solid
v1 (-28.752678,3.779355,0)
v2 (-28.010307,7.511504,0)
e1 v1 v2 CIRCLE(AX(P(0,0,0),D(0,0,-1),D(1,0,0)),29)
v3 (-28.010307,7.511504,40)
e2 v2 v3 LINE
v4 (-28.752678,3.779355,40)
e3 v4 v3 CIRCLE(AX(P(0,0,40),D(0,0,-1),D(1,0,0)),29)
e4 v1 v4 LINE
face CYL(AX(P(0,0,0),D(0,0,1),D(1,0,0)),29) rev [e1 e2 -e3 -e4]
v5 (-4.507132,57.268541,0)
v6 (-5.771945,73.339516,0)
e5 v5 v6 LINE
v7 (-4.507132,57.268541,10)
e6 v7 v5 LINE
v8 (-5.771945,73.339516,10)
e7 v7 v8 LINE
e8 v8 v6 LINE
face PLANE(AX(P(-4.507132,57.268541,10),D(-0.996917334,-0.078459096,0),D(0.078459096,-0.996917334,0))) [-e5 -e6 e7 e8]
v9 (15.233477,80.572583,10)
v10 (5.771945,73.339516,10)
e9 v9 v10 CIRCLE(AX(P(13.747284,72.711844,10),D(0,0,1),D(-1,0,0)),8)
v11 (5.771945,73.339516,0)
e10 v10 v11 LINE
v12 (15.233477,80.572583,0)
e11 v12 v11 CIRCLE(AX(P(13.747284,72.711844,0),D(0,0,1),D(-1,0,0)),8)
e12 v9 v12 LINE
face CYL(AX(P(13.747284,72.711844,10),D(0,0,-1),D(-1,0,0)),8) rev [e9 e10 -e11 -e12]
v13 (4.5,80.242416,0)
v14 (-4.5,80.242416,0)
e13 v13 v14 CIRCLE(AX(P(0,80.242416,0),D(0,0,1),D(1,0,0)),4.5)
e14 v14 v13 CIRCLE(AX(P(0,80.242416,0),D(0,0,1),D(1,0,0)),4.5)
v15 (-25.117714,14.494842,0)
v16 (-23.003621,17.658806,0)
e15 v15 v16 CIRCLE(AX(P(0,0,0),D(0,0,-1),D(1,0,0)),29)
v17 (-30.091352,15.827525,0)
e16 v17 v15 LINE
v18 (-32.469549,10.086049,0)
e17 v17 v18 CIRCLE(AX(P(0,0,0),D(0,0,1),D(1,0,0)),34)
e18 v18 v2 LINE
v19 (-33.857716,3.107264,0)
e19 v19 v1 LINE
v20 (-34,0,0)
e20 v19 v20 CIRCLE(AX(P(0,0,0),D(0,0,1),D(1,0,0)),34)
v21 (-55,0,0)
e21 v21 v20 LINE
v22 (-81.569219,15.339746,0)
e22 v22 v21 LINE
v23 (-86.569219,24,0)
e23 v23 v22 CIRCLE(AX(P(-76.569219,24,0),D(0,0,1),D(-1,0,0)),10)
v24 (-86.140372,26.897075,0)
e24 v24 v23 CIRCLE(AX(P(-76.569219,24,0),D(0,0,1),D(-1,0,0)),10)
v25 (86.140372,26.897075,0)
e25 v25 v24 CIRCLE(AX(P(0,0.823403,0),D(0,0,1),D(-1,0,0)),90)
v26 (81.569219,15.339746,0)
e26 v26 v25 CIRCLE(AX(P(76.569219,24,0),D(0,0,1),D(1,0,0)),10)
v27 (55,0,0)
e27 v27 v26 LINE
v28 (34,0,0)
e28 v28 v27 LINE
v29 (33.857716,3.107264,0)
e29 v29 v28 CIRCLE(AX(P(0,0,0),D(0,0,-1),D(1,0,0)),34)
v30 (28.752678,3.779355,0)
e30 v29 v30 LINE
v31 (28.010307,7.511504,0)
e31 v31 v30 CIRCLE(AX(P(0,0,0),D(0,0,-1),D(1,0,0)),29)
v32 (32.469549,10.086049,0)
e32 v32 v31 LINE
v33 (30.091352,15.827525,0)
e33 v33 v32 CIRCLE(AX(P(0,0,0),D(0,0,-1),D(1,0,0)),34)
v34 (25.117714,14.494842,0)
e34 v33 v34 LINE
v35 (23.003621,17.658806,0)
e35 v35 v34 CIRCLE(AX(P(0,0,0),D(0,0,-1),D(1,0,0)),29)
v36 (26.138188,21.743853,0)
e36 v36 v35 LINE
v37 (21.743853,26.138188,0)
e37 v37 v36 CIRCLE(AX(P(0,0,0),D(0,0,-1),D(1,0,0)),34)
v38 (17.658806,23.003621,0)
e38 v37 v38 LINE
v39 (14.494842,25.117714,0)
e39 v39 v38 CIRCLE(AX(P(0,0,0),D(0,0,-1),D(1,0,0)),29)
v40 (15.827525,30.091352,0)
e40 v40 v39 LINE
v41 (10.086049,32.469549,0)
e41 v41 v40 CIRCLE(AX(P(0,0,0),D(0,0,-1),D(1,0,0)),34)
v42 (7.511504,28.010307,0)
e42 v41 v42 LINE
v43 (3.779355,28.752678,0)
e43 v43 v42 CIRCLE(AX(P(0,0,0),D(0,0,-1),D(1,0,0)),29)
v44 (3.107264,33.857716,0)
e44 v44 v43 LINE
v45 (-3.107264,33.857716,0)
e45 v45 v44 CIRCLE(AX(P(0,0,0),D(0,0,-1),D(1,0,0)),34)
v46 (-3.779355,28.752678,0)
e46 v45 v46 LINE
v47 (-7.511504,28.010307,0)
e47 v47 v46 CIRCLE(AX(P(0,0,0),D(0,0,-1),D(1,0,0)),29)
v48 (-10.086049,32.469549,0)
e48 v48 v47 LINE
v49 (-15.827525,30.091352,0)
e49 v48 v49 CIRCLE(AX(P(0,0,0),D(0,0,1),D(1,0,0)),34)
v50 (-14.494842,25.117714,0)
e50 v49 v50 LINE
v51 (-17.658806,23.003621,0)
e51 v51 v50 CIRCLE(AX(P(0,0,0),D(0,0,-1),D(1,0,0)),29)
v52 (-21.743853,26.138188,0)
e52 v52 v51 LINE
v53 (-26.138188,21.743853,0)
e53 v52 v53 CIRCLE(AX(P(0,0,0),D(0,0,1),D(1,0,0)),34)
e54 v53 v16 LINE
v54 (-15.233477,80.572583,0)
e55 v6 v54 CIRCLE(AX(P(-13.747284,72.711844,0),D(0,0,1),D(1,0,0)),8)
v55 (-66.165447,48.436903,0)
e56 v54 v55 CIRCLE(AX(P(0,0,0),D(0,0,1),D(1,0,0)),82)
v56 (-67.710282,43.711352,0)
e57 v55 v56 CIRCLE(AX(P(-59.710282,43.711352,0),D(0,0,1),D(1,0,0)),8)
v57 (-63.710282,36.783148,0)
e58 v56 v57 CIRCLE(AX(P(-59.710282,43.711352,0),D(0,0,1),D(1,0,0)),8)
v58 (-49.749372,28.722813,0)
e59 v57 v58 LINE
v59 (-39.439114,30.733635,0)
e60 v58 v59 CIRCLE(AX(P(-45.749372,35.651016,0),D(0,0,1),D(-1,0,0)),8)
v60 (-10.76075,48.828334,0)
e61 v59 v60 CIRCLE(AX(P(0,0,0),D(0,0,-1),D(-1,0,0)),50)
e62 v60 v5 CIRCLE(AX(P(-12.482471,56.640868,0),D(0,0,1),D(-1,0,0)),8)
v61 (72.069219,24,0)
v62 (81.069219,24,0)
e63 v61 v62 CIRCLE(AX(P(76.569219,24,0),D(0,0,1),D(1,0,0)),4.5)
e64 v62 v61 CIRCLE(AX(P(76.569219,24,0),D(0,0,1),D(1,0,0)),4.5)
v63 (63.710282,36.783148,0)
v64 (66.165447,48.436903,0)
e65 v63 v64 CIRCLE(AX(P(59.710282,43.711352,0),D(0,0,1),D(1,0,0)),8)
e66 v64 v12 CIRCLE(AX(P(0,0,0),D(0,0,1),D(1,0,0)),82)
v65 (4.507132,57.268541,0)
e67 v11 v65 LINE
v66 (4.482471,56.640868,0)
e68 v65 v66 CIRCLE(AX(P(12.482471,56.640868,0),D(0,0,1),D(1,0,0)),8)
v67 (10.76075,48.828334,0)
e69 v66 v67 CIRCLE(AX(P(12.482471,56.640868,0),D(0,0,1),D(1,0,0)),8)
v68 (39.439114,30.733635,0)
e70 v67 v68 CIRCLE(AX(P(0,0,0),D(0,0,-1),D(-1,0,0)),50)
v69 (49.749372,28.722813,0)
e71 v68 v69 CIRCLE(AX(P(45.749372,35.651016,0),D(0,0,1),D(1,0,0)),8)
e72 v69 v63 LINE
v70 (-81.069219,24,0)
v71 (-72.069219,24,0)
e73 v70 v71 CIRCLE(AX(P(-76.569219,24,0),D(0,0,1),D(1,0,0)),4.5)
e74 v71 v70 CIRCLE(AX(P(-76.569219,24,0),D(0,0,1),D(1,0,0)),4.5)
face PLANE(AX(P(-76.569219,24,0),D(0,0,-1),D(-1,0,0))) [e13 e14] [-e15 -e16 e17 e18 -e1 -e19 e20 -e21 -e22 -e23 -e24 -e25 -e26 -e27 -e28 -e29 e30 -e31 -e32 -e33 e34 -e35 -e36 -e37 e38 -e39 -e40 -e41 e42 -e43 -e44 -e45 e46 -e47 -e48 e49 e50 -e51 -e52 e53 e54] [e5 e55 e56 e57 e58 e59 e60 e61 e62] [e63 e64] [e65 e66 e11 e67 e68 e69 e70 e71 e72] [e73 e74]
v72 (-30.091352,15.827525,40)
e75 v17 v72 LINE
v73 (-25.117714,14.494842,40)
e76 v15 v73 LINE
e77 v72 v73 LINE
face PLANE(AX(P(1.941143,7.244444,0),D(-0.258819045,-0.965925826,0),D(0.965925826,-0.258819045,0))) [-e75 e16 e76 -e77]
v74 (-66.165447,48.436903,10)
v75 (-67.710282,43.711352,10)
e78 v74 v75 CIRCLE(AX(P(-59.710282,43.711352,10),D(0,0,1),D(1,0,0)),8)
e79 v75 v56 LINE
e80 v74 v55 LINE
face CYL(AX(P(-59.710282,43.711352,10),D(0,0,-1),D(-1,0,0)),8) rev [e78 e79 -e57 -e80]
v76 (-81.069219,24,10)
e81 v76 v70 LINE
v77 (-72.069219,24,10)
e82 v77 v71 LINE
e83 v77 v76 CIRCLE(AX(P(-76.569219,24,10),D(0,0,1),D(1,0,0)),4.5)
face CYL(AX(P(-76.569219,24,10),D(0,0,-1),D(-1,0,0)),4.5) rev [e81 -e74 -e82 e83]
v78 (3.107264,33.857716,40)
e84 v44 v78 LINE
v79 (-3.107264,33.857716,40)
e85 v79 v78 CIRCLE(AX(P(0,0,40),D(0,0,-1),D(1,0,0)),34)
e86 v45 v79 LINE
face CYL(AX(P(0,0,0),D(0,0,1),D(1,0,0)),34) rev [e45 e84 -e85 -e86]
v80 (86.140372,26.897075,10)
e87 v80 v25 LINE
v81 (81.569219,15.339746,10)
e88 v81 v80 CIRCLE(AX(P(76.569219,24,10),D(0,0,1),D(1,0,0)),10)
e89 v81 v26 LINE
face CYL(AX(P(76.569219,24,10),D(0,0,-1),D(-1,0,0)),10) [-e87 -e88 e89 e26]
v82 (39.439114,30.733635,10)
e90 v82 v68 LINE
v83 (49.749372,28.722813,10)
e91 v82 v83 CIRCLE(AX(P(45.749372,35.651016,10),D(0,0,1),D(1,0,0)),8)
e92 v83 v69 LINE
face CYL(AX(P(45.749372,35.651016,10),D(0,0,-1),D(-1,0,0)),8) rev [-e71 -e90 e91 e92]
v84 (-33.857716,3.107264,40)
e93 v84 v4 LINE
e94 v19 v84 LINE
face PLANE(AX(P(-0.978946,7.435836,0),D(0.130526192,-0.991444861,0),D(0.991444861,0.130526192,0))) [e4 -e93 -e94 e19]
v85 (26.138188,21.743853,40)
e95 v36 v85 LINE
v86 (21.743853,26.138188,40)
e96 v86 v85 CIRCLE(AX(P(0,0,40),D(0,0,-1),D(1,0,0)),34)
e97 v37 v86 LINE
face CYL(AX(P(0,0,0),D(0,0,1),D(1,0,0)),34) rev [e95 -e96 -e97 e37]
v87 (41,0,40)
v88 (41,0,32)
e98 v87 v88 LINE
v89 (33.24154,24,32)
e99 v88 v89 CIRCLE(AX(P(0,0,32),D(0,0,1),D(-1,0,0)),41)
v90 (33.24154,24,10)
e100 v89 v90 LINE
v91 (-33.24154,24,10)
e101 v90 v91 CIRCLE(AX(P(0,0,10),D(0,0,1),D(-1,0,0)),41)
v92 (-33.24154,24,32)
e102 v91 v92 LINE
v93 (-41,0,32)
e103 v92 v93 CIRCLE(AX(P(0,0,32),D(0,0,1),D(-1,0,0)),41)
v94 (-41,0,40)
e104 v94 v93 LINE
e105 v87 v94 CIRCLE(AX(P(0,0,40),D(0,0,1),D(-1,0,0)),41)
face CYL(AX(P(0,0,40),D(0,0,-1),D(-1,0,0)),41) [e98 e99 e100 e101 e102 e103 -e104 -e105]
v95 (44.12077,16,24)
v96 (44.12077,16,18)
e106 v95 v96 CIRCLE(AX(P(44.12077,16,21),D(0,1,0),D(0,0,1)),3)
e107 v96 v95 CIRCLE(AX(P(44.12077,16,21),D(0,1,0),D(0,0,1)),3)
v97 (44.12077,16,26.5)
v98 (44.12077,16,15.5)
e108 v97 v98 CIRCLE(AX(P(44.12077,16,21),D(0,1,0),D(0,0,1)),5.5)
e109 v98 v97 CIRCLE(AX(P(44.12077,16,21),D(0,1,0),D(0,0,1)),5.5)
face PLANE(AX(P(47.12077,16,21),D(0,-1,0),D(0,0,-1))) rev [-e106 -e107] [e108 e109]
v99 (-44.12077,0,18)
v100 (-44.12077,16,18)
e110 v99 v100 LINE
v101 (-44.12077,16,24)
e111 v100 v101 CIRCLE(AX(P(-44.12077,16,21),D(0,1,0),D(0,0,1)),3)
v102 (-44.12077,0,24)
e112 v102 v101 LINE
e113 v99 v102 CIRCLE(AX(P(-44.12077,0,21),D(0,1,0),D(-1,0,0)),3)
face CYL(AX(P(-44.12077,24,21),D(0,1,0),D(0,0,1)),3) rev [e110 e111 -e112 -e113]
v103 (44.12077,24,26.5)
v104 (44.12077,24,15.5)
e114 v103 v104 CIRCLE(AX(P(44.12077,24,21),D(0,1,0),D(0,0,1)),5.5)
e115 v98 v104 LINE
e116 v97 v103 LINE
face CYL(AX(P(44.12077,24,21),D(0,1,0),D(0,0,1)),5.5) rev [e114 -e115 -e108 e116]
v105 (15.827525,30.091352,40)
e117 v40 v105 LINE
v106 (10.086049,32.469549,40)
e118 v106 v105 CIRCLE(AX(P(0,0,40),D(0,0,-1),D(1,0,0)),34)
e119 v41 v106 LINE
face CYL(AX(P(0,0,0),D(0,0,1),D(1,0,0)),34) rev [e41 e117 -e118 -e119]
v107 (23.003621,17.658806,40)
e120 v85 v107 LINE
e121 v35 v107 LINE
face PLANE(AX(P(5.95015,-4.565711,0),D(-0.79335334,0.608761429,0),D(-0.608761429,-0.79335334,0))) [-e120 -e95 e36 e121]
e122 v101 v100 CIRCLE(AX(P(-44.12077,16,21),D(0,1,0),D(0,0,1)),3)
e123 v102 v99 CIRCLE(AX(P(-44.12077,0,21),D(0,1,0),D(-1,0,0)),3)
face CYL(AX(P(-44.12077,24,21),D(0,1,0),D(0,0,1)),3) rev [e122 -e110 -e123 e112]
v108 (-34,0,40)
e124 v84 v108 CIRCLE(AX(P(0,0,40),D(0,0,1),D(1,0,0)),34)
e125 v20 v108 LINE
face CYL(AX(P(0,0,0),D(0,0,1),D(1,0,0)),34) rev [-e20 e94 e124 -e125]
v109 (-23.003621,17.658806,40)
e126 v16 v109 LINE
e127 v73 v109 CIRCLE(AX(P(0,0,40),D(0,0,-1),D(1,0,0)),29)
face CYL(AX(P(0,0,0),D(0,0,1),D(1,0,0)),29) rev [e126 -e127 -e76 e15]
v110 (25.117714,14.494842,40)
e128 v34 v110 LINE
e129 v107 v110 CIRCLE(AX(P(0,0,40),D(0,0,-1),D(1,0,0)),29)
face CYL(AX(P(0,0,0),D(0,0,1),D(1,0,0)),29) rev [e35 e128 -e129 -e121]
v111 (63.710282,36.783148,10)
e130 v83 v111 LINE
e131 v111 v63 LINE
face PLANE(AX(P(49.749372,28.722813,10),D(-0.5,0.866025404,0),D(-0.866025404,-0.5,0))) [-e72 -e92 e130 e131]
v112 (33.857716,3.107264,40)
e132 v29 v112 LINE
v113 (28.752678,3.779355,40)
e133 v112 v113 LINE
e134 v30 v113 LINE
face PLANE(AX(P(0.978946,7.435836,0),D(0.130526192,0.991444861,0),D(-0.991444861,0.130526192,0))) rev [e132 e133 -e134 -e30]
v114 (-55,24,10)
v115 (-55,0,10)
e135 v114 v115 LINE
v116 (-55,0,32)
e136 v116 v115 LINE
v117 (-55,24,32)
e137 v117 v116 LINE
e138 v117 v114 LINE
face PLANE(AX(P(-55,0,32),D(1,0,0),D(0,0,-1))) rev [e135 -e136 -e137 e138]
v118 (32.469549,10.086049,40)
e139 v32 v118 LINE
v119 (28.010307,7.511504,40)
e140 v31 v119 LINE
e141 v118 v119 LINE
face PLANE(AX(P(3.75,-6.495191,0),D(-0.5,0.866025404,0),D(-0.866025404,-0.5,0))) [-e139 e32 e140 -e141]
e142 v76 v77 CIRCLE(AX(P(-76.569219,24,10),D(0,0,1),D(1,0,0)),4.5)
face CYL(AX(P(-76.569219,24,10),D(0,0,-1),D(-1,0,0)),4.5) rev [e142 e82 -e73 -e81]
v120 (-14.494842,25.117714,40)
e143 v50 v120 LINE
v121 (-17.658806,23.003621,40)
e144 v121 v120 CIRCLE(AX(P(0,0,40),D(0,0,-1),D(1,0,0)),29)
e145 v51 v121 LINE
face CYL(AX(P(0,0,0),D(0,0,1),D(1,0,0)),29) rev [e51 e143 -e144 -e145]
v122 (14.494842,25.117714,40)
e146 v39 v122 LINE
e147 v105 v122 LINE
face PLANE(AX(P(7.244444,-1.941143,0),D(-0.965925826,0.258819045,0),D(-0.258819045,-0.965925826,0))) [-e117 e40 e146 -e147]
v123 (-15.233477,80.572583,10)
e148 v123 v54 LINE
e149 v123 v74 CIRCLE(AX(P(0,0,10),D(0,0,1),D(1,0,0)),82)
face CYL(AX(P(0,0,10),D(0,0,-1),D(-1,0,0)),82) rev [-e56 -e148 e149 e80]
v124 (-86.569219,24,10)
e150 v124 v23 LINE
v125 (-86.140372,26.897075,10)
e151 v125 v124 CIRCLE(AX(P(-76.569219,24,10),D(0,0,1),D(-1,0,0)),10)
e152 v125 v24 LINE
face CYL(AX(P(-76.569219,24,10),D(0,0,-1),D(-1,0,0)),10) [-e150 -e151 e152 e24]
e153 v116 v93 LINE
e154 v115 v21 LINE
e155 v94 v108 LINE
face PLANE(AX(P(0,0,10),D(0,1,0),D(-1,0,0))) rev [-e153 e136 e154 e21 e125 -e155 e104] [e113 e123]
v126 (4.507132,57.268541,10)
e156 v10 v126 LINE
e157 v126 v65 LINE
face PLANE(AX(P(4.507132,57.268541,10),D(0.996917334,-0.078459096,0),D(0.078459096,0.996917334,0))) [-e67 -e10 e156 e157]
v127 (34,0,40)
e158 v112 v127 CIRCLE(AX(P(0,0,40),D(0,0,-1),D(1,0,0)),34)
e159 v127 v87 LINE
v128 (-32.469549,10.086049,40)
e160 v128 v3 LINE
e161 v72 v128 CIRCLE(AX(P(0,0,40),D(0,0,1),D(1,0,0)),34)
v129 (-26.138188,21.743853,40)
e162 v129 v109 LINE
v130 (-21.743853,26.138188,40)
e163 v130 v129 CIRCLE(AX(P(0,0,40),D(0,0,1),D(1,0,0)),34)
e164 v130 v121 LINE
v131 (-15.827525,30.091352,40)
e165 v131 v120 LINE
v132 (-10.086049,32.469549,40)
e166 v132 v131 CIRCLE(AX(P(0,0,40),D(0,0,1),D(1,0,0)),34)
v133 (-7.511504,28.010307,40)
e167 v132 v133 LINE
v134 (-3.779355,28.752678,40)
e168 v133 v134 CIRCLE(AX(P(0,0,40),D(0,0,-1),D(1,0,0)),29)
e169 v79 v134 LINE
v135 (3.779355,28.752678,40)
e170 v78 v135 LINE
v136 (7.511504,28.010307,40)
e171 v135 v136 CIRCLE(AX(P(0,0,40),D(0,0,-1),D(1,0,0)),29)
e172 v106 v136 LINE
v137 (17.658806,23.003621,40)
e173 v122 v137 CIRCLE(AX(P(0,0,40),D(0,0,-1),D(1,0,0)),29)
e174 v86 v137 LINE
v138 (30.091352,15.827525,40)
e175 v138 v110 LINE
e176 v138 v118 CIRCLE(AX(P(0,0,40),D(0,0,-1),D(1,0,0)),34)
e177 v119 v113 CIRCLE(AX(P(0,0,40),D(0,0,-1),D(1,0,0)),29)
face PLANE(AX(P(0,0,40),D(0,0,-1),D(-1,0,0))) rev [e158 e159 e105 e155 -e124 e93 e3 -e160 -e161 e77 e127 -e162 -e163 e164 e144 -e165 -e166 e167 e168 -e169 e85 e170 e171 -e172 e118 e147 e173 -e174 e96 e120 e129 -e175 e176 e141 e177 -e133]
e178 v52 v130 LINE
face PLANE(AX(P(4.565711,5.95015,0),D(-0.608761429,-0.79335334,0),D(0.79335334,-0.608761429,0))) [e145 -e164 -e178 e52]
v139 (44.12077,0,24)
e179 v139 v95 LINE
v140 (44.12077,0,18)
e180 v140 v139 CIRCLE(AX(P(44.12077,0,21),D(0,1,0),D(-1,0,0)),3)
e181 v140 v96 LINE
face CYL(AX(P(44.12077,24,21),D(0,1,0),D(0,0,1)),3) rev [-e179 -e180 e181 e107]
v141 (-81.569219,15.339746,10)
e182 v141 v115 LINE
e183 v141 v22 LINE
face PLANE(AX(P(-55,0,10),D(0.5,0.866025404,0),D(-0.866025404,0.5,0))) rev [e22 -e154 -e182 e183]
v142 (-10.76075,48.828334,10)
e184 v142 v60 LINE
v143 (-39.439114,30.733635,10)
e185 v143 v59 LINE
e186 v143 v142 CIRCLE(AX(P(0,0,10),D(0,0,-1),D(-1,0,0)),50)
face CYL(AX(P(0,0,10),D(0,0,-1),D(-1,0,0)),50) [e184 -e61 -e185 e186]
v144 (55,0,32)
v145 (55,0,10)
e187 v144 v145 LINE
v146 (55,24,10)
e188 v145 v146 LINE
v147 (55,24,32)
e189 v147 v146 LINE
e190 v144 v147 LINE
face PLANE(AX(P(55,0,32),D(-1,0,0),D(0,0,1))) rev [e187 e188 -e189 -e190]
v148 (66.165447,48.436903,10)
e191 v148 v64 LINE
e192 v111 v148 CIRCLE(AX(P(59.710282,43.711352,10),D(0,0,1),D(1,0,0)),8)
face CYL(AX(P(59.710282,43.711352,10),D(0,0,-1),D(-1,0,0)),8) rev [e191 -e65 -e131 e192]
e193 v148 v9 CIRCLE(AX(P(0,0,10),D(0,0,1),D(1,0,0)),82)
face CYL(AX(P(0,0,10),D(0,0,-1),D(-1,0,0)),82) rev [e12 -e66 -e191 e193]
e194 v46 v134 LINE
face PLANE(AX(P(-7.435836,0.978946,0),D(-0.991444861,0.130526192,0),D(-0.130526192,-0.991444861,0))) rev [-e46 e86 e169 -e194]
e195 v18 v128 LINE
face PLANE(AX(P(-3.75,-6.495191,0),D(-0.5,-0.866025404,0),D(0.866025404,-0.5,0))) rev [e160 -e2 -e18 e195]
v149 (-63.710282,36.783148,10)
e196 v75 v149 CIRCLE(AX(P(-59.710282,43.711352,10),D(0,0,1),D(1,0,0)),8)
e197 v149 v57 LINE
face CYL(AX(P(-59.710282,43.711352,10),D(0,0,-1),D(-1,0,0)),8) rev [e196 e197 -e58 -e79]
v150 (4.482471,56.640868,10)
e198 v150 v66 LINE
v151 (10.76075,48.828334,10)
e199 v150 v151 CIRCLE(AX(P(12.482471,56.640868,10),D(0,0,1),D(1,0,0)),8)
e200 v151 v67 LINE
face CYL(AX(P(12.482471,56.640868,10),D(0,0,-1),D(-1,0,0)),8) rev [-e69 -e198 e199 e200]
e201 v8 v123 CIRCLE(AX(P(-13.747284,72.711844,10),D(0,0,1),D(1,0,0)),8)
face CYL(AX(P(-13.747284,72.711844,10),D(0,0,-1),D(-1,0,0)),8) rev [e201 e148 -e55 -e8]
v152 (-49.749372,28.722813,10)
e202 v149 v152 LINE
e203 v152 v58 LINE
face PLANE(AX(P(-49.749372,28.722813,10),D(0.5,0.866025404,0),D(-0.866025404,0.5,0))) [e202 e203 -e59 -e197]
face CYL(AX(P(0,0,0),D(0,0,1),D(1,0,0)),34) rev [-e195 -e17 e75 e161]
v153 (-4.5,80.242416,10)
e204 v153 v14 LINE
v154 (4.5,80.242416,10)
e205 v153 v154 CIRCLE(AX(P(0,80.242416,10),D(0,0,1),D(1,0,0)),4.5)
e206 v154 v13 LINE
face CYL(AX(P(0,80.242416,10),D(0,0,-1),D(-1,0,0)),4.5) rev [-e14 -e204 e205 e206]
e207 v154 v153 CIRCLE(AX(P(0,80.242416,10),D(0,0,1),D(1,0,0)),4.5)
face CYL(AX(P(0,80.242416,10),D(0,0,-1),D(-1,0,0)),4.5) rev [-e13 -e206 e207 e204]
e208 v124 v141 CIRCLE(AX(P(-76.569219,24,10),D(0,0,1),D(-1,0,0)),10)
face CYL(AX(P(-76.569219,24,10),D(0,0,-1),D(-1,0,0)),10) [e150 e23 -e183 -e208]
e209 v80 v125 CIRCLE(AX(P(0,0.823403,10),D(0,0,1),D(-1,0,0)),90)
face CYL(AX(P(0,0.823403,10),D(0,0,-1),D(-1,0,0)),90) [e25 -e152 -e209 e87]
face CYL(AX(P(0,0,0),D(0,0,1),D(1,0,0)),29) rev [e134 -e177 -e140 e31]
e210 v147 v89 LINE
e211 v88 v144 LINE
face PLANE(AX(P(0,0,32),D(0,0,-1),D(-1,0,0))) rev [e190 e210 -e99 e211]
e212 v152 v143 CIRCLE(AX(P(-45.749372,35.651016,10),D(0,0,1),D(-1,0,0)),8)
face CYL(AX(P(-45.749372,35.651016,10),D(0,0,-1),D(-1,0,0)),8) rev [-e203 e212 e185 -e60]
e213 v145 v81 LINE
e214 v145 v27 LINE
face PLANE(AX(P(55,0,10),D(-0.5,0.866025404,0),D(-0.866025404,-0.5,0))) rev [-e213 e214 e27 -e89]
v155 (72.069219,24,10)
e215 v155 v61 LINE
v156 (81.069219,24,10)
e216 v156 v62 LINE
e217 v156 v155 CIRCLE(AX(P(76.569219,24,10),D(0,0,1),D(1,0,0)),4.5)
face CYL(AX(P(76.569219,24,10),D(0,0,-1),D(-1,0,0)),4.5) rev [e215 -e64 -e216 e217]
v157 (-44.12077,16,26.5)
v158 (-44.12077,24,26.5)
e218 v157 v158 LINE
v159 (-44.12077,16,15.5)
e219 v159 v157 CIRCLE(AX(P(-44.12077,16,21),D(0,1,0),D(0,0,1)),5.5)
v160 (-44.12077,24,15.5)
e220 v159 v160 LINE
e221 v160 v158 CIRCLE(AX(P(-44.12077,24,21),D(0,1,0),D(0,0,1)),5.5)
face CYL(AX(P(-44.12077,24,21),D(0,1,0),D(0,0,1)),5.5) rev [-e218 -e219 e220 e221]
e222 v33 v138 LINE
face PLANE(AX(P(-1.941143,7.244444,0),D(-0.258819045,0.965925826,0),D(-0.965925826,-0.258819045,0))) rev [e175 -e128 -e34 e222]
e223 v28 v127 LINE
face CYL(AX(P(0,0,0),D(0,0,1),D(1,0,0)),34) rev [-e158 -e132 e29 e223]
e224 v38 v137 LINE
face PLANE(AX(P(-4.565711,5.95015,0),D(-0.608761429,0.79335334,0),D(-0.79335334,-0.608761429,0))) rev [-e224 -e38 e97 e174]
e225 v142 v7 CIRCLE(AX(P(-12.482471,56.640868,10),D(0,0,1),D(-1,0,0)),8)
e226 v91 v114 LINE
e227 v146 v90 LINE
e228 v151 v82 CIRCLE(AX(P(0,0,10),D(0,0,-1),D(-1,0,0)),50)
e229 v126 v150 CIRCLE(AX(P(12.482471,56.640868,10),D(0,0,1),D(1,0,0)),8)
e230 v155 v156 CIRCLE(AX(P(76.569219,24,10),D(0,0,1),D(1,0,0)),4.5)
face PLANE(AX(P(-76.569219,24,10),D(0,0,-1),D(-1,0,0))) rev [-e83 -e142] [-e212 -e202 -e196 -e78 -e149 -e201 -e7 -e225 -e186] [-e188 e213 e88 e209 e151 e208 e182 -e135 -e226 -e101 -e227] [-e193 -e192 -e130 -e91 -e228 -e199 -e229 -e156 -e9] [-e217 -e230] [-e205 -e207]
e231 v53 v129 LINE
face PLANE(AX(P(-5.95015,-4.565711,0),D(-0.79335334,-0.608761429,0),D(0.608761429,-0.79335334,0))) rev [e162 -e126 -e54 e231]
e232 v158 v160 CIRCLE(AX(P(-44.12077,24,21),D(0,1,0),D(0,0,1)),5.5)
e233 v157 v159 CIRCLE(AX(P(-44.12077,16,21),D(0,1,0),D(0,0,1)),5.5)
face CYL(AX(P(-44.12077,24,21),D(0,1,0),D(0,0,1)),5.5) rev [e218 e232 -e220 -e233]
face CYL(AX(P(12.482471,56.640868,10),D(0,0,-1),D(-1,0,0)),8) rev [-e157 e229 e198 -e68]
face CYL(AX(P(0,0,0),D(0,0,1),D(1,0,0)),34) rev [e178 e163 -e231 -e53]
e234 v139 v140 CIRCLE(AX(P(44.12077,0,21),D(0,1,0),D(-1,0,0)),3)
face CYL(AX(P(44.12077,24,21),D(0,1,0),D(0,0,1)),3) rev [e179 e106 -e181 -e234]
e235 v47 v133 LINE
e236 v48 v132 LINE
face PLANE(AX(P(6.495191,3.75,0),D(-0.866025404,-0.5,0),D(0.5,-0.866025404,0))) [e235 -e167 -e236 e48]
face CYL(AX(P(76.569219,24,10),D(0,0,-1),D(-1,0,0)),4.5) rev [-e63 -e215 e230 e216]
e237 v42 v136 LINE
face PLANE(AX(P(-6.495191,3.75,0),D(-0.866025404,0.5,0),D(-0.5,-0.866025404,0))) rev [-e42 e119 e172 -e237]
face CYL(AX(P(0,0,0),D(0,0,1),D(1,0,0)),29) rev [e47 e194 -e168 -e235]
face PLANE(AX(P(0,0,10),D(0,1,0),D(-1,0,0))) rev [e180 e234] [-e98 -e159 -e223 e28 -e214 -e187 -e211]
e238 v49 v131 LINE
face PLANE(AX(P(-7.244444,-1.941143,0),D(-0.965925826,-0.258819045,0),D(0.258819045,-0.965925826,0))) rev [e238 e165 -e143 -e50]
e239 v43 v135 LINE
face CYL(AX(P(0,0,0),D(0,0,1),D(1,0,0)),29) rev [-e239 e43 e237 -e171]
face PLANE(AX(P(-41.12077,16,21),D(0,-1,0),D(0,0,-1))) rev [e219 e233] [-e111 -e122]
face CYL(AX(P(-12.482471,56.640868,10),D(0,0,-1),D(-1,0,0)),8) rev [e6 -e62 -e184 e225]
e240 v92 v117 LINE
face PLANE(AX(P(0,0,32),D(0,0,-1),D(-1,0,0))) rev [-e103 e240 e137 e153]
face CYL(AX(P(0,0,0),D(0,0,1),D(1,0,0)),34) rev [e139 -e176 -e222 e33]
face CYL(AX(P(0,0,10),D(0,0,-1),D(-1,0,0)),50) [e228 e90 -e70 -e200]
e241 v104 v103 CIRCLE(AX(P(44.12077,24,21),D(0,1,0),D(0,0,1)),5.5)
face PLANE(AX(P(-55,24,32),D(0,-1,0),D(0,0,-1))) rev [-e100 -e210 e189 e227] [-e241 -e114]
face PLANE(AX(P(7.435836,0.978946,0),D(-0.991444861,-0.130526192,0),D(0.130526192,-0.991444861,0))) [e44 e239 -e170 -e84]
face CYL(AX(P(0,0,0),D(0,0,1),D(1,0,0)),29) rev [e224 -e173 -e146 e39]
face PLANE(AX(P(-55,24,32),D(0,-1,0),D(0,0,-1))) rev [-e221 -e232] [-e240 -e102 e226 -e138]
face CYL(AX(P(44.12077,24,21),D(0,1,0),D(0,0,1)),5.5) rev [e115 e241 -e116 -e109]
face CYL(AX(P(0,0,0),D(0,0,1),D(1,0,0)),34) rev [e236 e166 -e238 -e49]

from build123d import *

# Parameters (mm, degrees)
SECTOR_PLATE_SKETCH_R          = 4.5
SECTOR_PLATE_DEPTH             = 10
MOUNTING_LUG_SKETCH_W          = 110
MOUNTING_LUG_SKETCH_H          = 24
MOUNTING_LUGS_DEPTH            = 22
HALF_HUB_DEPTH                 = 30
LUG_C_BORE_HOLES_6_D           = 6
LUG_C_BORE_HOLES_6_DEPTH       = 99.968745116
LUG_C_BORE_HOLES_6_CBORE_D     = 11
LUG_C_BORE_HOLES_6_CBORE_DEPTH = 8
INTERNAL_SPLINE_CUT_DEPTH      = 132.69328114


with BuildPart() as part:
    # Sector Plate Sketch → Sector Plate (new body)
    with BuildSketch(Plane.XY):
        with BuildLine():
            Line((0, 0), (55, 0))
            Line((55, 0), (81.569219382, 15.339745962))
            ThreePointArc((81.569219382, 15.339745962), (85.868282889, 20.322036175), (86.140371804, 26.897074611))
            ThreePointArc((86.140371804, 26.897074611), (0, 90.823403113), (-86.140371804, 26.897074611))
            ThreePointArc((-86.140371804, 26.897074611), (-85.868282889, 20.322036175), (-81.569219382, 15.339745962))
            Line((-81.569219382, 15.339745962), (-55, 0))
            Line((-55, 0), (0, 0))
        make_face()
        with Locations((-76.569219382, 24)):
            Circle(SECTOR_PLATE_SKETCH_R, mode=Mode.SUBTRACT)
        with Locations((76.569219382, 24)):
            Circle(SECTOR_PLATE_SKETCH_R, mode=Mode.SUBTRACT)
        with Locations((0, 80.242416194)):
            Circle(SECTOR_PLATE_SKETCH_R, mode=Mode.SUBTRACT)
        with BuildLine():
            Line((4.507131906, 57.26854077), (5.77194511, 73.33951629))
            ThreePointArc((5.77194511, 73.33951629), (8.888624682, 79.067426249), (15.233476621, 80.572583365))
            ThreePointArc((15.233476621, 80.572583365), (43.756390305, 69.34968138), (66.165447339, 48.436903064))
            ThreePointArc((66.165447339, 48.436903064), (67.538443843, 42.062146233), (63.710281745, 36.783148315))
            Line((63.710281745, 36.783148315), (49.749371855, 28.722813233))
            ThreePointArc((49.749371855, 28.722813233), (44.217975712, 27.798957762), (39.439113668, 30.733634882))
            ThreePointArc((39.439113668, 30.733634882), (26.680725796, 42.286391085), (10.760750496, 48.828334487))
            ThreePointArc((10.760750496, 48.828334487), (6.054600974, 51.878253977), (4.507131906, 57.26854077))
        make_face(mode=Mode.SUBTRACT)
        with BuildLine():
            Line((-4.507131906, 57.26854077), (-5.77194511, 73.33951629))
            ThreePointArc((-5.77194511, 73.33951629), (-8.888624682, 79.067426249), (-15.233476621, 80.572583365))
            ThreePointArc((-15.233476621, 80.572583365), (-43.756390305, 69.34968138), (-66.165447339, 48.436903064))
            ThreePointArc((-66.165447339, 48.436903064), (-67.538443843, 42.062146233), (-63.710281745, 36.783148315))
            Line((-63.710281745, 36.783148315), (-49.749371855, 28.722813233))
            ThreePointArc((-49.749371855, 28.722813233), (-44.217975712, 27.798957762), (-39.439113668, 30.733634882))
            ThreePointArc((-39.439113668, 30.733634882), (-26.680725796, 42.286391085), (-10.760750496, 48.828334487))
            ThreePointArc((-10.760750496, 48.828334487), (-6.054600974, 51.878253977), (-4.507131906, 57.26854077))
        make_face(mode=Mode.SUBTRACT)
    extrude(amount=SECTOR_PLATE_DEPTH)

    # Mounting Lug Sketch → Mounting Lugs (add)
    with BuildSketch(Plane.XY.offset(10)):
        with Locations((0, 12)):
            Rectangle(MOUNTING_LUG_SKETCH_W, MOUNTING_LUG_SKETCH_H)
    extrude(amount=MOUNTING_LUGS_DEPTH)

    # Half Hub Sketch → Half Hub (add)
    with BuildSketch(Plane.XY.offset(10)):
        with BuildLine():
            Line((-41, 0), (41, 0))
            ThreePointArc((41, 0), (0, 41), (-41, 0))
        make_face()
    extrude(amount=HALF_HUB_DEPTH)

    # Lug C'Bore Holes Ø6
    with Locations(Plane(origin=(-44.120770139, 24, 21), x_dir=(0, 0, 1), z_dir=(0, 1, 0))):
        with Locations((0, 0), (0, 88.241540278)):
            CounterBoreHole(LUG_C_BORE_HOLES_6_D / 2, LUG_C_BORE_HOLES_6_CBORE_D / 2, LUG_C_BORE_HOLES_6_CBORE_DEPTH, depth=LUG_C_BORE_HOLES_6_DEPTH)

    # Internal Spline Sketch → Internal Spline Cut (cut, through all)
    with BuildSketch(Plane.XY.offset(40)):
        with BuildLine():
            ThreePointArc((3.107264378, 33.857715636), (0, 34), (-3.107264378, 33.857715636))
            Line((-3.107264378, 33.857715636), (-3.779355377, 28.752677665))
            ThreePointArc((-3.779355377, 28.752677665), (-5.657619338, 28.442773132), (-7.511504299, 28.010307088))
            Line((-7.511504299, 28.010307088), (-10.08604887, 32.469549091))
            ThreePointArc((-10.08604887, 32.469549091), (-13.0112367, 31.411904105), (-15.827524793, 30.091351896))
            Line((-15.827524793, 30.091351896), (-14.494842458, 25.117713712))
            ThreePointArc((-14.494842458, 25.117713712), (-16.111536758, 24.112618757), (-17.658805539, 23.00362117))
            Line((-17.658805539, 23.00362117), (-21.743852609, 26.138188034))
            ThreePointArc((-21.743852609, 26.138188034), (-24.04163056, 24.04163056), (-26.138188034, 21.743852609))
            Line((-26.138188034, 21.743852609), (-23.00362117, 17.658805539))
            ThreePointArc((-23.00362117, 17.658805539), (-24.112618757, 16.111536758), (-25.117713712, 14.494842458))
            Line((-25.117713712, 14.494842458), (-30.091351896, 15.827524793))
            ThreePointArc((-30.091351896, 15.827524793), (-31.411904105, 13.0112367), (-32.469549091, 10.08604887))
            Line((-32.469549091, 10.08604887), (-28.010307088, 7.511504299))
            ThreePointArc((-28.010307088, 7.511504299), (-28.442773132, 5.657619338), (-28.752677665, 3.779355377))
            Line((-28.752677665, 3.779355377), (-33.857715636, 3.107264378))
            ThreePointArc((-33.857715636, 3.107264378), (-33.964410282, 1.555260168), (-34, 0))
            Line((-34, 0), (34, 0))
            ThreePointArc((34, 0), (33.964410282, 1.555260168), (33.857715636, 3.107264378))
            Line((33.857715636, 3.107264378), (28.752677665, 3.779355377))
            ThreePointArc((28.752677665, 3.779355377), (28.442773132, 5.657619338), (28.010307088, 7.511504299))
            Line((28.010307088, 7.511504299), (32.469549091, 10.08604887))
            ThreePointArc((32.469549091, 10.08604887), (31.411904105, 13.0112367), (30.091351896, 15.827524793))
            Line((30.091351896, 15.827524793), (25.117713712, 14.494842458))
            ThreePointArc((25.117713712, 14.494842458), (24.112618757, 16.111536758), (23.00362117, 17.658805539))
            Line((23.00362117, 17.658805539), (26.138188034, 21.743852609))
            ThreePointArc((26.138188034, 21.743852609), (24.04163056, 24.04163056), (21.743852609, 26.138188034))
            Line((21.743852609, 26.138188034), (17.658805539, 23.00362117))
            ThreePointArc((17.658805539, 23.00362117), (16.111536758, 24.112618757), (14.494842458, 25.117713712))
            Line((14.494842458, 25.117713712), (15.827524793, 30.091351896))
            ThreePointArc((15.827524793, 30.091351896), (13.0112367, 31.411904105), (10.08604887, 32.469549091))
            Line((10.08604887, 32.469549091), (7.511504299, 28.010307088))
            ThreePointArc((7.511504299, 28.010307088), (5.657619338, 28.442773132), (3.779355377, 28.752677665))
            Line((3.779355377, 28.752677665), (3.107264378, 33.857715636))
        make_face()
    extrude(amount=-INTERNAL_SPLINE_CUT_DEPTH, mode=Mode.SUBTRACT)


solid = part.part
